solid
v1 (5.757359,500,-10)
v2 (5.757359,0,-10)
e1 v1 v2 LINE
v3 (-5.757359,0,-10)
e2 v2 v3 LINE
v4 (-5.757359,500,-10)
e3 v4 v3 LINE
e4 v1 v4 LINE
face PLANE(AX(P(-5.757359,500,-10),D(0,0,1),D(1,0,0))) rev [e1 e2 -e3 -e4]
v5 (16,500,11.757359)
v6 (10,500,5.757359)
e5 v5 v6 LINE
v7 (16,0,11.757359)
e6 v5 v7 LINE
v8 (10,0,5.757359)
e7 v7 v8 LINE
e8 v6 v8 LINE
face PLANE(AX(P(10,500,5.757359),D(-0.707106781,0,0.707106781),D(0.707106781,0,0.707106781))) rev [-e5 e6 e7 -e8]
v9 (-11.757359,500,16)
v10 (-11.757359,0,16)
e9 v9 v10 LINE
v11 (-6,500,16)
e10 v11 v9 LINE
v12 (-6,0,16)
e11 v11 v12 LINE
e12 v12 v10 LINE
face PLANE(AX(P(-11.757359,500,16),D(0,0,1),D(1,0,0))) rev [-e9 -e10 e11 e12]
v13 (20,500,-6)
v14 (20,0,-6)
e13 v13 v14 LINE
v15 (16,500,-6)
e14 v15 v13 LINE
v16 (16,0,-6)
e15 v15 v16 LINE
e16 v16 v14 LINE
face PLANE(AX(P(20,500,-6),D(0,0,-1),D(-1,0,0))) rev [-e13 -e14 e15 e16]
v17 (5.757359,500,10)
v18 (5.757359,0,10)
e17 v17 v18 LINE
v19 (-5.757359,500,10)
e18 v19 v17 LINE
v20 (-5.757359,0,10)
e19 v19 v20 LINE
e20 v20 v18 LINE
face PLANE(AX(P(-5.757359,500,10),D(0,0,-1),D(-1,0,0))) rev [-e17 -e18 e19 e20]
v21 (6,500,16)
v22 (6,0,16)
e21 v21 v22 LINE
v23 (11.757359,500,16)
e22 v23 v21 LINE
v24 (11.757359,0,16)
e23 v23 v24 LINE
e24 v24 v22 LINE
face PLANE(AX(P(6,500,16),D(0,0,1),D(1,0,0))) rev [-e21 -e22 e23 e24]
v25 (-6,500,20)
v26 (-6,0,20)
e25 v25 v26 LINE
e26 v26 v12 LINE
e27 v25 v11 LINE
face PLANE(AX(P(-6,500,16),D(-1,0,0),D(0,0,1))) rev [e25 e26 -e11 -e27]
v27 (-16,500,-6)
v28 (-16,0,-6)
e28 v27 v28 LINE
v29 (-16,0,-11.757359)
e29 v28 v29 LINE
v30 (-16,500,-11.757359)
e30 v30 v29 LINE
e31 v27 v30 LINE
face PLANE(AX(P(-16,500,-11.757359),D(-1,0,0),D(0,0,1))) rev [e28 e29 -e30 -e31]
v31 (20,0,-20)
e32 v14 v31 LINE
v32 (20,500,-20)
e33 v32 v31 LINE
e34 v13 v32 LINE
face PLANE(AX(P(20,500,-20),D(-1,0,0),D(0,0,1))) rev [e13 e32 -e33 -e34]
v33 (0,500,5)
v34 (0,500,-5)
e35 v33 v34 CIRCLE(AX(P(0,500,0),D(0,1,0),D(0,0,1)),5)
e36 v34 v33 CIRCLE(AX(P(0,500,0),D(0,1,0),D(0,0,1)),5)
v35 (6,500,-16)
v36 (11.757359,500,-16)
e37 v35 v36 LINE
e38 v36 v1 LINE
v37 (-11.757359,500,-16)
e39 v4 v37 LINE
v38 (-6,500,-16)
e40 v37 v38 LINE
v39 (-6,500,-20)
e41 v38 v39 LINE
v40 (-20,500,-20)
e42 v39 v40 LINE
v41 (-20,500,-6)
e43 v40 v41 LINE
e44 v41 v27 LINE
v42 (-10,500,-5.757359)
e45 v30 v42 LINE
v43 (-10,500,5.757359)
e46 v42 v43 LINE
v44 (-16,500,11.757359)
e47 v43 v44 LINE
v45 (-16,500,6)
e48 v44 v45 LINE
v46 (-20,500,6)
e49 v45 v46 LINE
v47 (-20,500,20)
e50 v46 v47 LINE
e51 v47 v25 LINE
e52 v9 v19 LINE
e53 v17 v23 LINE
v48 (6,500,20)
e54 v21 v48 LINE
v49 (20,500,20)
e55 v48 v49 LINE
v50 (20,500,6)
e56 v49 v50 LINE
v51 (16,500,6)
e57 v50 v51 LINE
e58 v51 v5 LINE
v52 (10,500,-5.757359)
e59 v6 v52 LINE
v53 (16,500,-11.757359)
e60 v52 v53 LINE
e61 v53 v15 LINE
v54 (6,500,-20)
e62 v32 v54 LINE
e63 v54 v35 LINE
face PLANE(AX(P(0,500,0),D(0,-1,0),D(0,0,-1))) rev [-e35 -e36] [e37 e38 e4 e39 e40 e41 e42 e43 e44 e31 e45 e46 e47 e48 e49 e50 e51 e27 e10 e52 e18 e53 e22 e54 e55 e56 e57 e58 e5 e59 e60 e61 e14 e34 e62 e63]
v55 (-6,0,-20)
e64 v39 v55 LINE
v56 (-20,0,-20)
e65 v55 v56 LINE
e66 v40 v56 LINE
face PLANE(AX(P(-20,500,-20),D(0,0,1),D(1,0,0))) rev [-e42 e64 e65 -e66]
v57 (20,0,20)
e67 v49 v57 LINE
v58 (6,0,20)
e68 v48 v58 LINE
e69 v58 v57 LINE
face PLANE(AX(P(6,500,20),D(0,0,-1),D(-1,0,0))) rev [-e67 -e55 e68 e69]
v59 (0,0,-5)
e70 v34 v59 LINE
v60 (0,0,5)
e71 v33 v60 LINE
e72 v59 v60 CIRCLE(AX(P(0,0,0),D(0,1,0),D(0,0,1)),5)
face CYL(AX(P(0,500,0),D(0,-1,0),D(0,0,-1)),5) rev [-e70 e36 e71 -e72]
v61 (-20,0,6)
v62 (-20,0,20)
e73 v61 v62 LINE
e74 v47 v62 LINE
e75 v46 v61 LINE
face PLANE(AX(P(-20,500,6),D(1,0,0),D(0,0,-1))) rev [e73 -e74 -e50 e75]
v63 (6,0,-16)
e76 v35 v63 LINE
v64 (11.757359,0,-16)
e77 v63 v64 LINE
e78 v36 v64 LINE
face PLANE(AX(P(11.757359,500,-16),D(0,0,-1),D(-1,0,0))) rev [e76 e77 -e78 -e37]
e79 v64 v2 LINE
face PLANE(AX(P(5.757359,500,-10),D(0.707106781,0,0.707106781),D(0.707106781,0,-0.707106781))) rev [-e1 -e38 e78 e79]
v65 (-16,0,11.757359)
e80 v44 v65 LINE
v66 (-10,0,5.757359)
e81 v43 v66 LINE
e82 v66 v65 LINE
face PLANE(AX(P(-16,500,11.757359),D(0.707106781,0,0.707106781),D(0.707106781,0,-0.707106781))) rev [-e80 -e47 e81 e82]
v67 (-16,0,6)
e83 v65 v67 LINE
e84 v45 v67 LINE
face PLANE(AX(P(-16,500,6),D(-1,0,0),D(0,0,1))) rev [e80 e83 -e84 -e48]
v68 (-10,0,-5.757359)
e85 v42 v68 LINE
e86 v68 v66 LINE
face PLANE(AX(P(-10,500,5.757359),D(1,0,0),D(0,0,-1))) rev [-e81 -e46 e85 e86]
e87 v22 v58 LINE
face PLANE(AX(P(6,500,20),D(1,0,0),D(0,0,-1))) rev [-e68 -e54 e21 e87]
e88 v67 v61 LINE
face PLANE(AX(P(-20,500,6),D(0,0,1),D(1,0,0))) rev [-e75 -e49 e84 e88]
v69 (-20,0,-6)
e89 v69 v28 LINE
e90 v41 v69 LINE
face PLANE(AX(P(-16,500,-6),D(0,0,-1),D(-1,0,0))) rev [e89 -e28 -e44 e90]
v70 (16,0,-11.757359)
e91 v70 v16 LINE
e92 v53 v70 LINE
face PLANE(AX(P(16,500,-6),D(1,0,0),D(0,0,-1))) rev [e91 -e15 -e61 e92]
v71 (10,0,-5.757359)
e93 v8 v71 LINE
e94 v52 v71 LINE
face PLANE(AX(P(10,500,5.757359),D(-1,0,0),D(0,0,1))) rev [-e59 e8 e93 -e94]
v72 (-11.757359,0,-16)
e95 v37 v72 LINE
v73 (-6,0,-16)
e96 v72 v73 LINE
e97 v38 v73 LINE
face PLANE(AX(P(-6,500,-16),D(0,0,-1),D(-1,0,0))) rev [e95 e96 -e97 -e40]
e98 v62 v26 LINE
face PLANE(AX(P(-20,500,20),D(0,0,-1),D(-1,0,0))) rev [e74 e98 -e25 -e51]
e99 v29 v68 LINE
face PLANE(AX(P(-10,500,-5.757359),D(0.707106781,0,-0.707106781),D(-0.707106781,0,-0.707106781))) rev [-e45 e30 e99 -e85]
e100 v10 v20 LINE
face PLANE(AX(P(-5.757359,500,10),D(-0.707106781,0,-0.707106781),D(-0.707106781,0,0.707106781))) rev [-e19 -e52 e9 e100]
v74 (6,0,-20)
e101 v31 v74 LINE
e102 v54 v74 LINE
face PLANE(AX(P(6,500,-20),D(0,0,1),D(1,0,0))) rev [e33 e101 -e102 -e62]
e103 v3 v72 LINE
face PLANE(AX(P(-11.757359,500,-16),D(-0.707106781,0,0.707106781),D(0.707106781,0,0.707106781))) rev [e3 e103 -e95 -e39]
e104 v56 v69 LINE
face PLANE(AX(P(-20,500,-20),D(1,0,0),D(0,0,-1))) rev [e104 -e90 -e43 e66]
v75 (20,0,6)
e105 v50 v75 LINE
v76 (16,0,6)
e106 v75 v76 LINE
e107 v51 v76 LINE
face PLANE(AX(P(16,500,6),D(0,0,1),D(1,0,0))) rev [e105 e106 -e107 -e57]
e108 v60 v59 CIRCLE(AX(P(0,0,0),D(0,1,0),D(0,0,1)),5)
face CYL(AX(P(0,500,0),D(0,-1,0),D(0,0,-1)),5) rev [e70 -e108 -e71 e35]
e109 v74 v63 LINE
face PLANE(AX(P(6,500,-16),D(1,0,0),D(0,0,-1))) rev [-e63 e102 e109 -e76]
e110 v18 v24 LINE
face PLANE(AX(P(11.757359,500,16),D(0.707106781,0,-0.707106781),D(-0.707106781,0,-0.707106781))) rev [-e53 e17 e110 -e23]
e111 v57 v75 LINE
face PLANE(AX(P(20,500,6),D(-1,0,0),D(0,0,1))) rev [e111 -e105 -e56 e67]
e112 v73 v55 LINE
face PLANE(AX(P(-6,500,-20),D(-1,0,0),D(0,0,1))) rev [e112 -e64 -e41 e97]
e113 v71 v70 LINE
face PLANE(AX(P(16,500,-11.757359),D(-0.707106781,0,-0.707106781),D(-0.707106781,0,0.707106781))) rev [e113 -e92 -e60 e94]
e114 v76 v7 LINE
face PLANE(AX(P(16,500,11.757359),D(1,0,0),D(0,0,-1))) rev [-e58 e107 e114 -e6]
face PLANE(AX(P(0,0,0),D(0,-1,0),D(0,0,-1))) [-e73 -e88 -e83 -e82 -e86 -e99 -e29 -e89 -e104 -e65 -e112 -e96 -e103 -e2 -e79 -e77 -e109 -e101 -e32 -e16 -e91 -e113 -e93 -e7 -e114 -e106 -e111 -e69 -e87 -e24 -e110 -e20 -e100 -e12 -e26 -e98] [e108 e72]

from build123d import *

# Parameters (mm, degrees)
SKETCH1_R           = 5
BOSS_EXTRUDE1_DEPTH = 500


with BuildPart() as part:
    # Sketch1 → Boss-Extrude1 (new body)
    with BuildSketch(Plane(origin=(0, 0, 0), x_dir=(1, 0, 0), z_dir=(0, 1, 0))):
        Polygon((-6, 20), (-6, 16), (-11.757359313, 16), (-5.757359313, 10), (5.757359313, 10), (11.757359313, 16), (6, 16), (6, 20), (20, 20), (20, 6), (16, 6), (16, 11.757359313), (10, 5.757359313), (10, -5.757359313), (16, -11.757359313), (16, -6), (20, -6), (20, -20), (6, -20), (6, -16), (11.757359313, -16), (5.757359313, -10), (-5.757359313, -10), (-11.757359313, -16), (-6, -16), (-6, -20), (-20, -20), (-20, -6), (-16, -6), (-16, -11.757359313), (-10, -5.757359313), (-10, 5.757359313), (-16, 11.757359313), (-16, 6), (-20, 6), (-20, 20), align=None)
        with Locations(Location((0, 0, 0), (0, 0, 270))):
            Circle(SKETCH1_R, mode=Mode.SUBTRACT)
    extrude(amount=BOSS_EXTRUDE1_DEPTH)


solid = part.part
